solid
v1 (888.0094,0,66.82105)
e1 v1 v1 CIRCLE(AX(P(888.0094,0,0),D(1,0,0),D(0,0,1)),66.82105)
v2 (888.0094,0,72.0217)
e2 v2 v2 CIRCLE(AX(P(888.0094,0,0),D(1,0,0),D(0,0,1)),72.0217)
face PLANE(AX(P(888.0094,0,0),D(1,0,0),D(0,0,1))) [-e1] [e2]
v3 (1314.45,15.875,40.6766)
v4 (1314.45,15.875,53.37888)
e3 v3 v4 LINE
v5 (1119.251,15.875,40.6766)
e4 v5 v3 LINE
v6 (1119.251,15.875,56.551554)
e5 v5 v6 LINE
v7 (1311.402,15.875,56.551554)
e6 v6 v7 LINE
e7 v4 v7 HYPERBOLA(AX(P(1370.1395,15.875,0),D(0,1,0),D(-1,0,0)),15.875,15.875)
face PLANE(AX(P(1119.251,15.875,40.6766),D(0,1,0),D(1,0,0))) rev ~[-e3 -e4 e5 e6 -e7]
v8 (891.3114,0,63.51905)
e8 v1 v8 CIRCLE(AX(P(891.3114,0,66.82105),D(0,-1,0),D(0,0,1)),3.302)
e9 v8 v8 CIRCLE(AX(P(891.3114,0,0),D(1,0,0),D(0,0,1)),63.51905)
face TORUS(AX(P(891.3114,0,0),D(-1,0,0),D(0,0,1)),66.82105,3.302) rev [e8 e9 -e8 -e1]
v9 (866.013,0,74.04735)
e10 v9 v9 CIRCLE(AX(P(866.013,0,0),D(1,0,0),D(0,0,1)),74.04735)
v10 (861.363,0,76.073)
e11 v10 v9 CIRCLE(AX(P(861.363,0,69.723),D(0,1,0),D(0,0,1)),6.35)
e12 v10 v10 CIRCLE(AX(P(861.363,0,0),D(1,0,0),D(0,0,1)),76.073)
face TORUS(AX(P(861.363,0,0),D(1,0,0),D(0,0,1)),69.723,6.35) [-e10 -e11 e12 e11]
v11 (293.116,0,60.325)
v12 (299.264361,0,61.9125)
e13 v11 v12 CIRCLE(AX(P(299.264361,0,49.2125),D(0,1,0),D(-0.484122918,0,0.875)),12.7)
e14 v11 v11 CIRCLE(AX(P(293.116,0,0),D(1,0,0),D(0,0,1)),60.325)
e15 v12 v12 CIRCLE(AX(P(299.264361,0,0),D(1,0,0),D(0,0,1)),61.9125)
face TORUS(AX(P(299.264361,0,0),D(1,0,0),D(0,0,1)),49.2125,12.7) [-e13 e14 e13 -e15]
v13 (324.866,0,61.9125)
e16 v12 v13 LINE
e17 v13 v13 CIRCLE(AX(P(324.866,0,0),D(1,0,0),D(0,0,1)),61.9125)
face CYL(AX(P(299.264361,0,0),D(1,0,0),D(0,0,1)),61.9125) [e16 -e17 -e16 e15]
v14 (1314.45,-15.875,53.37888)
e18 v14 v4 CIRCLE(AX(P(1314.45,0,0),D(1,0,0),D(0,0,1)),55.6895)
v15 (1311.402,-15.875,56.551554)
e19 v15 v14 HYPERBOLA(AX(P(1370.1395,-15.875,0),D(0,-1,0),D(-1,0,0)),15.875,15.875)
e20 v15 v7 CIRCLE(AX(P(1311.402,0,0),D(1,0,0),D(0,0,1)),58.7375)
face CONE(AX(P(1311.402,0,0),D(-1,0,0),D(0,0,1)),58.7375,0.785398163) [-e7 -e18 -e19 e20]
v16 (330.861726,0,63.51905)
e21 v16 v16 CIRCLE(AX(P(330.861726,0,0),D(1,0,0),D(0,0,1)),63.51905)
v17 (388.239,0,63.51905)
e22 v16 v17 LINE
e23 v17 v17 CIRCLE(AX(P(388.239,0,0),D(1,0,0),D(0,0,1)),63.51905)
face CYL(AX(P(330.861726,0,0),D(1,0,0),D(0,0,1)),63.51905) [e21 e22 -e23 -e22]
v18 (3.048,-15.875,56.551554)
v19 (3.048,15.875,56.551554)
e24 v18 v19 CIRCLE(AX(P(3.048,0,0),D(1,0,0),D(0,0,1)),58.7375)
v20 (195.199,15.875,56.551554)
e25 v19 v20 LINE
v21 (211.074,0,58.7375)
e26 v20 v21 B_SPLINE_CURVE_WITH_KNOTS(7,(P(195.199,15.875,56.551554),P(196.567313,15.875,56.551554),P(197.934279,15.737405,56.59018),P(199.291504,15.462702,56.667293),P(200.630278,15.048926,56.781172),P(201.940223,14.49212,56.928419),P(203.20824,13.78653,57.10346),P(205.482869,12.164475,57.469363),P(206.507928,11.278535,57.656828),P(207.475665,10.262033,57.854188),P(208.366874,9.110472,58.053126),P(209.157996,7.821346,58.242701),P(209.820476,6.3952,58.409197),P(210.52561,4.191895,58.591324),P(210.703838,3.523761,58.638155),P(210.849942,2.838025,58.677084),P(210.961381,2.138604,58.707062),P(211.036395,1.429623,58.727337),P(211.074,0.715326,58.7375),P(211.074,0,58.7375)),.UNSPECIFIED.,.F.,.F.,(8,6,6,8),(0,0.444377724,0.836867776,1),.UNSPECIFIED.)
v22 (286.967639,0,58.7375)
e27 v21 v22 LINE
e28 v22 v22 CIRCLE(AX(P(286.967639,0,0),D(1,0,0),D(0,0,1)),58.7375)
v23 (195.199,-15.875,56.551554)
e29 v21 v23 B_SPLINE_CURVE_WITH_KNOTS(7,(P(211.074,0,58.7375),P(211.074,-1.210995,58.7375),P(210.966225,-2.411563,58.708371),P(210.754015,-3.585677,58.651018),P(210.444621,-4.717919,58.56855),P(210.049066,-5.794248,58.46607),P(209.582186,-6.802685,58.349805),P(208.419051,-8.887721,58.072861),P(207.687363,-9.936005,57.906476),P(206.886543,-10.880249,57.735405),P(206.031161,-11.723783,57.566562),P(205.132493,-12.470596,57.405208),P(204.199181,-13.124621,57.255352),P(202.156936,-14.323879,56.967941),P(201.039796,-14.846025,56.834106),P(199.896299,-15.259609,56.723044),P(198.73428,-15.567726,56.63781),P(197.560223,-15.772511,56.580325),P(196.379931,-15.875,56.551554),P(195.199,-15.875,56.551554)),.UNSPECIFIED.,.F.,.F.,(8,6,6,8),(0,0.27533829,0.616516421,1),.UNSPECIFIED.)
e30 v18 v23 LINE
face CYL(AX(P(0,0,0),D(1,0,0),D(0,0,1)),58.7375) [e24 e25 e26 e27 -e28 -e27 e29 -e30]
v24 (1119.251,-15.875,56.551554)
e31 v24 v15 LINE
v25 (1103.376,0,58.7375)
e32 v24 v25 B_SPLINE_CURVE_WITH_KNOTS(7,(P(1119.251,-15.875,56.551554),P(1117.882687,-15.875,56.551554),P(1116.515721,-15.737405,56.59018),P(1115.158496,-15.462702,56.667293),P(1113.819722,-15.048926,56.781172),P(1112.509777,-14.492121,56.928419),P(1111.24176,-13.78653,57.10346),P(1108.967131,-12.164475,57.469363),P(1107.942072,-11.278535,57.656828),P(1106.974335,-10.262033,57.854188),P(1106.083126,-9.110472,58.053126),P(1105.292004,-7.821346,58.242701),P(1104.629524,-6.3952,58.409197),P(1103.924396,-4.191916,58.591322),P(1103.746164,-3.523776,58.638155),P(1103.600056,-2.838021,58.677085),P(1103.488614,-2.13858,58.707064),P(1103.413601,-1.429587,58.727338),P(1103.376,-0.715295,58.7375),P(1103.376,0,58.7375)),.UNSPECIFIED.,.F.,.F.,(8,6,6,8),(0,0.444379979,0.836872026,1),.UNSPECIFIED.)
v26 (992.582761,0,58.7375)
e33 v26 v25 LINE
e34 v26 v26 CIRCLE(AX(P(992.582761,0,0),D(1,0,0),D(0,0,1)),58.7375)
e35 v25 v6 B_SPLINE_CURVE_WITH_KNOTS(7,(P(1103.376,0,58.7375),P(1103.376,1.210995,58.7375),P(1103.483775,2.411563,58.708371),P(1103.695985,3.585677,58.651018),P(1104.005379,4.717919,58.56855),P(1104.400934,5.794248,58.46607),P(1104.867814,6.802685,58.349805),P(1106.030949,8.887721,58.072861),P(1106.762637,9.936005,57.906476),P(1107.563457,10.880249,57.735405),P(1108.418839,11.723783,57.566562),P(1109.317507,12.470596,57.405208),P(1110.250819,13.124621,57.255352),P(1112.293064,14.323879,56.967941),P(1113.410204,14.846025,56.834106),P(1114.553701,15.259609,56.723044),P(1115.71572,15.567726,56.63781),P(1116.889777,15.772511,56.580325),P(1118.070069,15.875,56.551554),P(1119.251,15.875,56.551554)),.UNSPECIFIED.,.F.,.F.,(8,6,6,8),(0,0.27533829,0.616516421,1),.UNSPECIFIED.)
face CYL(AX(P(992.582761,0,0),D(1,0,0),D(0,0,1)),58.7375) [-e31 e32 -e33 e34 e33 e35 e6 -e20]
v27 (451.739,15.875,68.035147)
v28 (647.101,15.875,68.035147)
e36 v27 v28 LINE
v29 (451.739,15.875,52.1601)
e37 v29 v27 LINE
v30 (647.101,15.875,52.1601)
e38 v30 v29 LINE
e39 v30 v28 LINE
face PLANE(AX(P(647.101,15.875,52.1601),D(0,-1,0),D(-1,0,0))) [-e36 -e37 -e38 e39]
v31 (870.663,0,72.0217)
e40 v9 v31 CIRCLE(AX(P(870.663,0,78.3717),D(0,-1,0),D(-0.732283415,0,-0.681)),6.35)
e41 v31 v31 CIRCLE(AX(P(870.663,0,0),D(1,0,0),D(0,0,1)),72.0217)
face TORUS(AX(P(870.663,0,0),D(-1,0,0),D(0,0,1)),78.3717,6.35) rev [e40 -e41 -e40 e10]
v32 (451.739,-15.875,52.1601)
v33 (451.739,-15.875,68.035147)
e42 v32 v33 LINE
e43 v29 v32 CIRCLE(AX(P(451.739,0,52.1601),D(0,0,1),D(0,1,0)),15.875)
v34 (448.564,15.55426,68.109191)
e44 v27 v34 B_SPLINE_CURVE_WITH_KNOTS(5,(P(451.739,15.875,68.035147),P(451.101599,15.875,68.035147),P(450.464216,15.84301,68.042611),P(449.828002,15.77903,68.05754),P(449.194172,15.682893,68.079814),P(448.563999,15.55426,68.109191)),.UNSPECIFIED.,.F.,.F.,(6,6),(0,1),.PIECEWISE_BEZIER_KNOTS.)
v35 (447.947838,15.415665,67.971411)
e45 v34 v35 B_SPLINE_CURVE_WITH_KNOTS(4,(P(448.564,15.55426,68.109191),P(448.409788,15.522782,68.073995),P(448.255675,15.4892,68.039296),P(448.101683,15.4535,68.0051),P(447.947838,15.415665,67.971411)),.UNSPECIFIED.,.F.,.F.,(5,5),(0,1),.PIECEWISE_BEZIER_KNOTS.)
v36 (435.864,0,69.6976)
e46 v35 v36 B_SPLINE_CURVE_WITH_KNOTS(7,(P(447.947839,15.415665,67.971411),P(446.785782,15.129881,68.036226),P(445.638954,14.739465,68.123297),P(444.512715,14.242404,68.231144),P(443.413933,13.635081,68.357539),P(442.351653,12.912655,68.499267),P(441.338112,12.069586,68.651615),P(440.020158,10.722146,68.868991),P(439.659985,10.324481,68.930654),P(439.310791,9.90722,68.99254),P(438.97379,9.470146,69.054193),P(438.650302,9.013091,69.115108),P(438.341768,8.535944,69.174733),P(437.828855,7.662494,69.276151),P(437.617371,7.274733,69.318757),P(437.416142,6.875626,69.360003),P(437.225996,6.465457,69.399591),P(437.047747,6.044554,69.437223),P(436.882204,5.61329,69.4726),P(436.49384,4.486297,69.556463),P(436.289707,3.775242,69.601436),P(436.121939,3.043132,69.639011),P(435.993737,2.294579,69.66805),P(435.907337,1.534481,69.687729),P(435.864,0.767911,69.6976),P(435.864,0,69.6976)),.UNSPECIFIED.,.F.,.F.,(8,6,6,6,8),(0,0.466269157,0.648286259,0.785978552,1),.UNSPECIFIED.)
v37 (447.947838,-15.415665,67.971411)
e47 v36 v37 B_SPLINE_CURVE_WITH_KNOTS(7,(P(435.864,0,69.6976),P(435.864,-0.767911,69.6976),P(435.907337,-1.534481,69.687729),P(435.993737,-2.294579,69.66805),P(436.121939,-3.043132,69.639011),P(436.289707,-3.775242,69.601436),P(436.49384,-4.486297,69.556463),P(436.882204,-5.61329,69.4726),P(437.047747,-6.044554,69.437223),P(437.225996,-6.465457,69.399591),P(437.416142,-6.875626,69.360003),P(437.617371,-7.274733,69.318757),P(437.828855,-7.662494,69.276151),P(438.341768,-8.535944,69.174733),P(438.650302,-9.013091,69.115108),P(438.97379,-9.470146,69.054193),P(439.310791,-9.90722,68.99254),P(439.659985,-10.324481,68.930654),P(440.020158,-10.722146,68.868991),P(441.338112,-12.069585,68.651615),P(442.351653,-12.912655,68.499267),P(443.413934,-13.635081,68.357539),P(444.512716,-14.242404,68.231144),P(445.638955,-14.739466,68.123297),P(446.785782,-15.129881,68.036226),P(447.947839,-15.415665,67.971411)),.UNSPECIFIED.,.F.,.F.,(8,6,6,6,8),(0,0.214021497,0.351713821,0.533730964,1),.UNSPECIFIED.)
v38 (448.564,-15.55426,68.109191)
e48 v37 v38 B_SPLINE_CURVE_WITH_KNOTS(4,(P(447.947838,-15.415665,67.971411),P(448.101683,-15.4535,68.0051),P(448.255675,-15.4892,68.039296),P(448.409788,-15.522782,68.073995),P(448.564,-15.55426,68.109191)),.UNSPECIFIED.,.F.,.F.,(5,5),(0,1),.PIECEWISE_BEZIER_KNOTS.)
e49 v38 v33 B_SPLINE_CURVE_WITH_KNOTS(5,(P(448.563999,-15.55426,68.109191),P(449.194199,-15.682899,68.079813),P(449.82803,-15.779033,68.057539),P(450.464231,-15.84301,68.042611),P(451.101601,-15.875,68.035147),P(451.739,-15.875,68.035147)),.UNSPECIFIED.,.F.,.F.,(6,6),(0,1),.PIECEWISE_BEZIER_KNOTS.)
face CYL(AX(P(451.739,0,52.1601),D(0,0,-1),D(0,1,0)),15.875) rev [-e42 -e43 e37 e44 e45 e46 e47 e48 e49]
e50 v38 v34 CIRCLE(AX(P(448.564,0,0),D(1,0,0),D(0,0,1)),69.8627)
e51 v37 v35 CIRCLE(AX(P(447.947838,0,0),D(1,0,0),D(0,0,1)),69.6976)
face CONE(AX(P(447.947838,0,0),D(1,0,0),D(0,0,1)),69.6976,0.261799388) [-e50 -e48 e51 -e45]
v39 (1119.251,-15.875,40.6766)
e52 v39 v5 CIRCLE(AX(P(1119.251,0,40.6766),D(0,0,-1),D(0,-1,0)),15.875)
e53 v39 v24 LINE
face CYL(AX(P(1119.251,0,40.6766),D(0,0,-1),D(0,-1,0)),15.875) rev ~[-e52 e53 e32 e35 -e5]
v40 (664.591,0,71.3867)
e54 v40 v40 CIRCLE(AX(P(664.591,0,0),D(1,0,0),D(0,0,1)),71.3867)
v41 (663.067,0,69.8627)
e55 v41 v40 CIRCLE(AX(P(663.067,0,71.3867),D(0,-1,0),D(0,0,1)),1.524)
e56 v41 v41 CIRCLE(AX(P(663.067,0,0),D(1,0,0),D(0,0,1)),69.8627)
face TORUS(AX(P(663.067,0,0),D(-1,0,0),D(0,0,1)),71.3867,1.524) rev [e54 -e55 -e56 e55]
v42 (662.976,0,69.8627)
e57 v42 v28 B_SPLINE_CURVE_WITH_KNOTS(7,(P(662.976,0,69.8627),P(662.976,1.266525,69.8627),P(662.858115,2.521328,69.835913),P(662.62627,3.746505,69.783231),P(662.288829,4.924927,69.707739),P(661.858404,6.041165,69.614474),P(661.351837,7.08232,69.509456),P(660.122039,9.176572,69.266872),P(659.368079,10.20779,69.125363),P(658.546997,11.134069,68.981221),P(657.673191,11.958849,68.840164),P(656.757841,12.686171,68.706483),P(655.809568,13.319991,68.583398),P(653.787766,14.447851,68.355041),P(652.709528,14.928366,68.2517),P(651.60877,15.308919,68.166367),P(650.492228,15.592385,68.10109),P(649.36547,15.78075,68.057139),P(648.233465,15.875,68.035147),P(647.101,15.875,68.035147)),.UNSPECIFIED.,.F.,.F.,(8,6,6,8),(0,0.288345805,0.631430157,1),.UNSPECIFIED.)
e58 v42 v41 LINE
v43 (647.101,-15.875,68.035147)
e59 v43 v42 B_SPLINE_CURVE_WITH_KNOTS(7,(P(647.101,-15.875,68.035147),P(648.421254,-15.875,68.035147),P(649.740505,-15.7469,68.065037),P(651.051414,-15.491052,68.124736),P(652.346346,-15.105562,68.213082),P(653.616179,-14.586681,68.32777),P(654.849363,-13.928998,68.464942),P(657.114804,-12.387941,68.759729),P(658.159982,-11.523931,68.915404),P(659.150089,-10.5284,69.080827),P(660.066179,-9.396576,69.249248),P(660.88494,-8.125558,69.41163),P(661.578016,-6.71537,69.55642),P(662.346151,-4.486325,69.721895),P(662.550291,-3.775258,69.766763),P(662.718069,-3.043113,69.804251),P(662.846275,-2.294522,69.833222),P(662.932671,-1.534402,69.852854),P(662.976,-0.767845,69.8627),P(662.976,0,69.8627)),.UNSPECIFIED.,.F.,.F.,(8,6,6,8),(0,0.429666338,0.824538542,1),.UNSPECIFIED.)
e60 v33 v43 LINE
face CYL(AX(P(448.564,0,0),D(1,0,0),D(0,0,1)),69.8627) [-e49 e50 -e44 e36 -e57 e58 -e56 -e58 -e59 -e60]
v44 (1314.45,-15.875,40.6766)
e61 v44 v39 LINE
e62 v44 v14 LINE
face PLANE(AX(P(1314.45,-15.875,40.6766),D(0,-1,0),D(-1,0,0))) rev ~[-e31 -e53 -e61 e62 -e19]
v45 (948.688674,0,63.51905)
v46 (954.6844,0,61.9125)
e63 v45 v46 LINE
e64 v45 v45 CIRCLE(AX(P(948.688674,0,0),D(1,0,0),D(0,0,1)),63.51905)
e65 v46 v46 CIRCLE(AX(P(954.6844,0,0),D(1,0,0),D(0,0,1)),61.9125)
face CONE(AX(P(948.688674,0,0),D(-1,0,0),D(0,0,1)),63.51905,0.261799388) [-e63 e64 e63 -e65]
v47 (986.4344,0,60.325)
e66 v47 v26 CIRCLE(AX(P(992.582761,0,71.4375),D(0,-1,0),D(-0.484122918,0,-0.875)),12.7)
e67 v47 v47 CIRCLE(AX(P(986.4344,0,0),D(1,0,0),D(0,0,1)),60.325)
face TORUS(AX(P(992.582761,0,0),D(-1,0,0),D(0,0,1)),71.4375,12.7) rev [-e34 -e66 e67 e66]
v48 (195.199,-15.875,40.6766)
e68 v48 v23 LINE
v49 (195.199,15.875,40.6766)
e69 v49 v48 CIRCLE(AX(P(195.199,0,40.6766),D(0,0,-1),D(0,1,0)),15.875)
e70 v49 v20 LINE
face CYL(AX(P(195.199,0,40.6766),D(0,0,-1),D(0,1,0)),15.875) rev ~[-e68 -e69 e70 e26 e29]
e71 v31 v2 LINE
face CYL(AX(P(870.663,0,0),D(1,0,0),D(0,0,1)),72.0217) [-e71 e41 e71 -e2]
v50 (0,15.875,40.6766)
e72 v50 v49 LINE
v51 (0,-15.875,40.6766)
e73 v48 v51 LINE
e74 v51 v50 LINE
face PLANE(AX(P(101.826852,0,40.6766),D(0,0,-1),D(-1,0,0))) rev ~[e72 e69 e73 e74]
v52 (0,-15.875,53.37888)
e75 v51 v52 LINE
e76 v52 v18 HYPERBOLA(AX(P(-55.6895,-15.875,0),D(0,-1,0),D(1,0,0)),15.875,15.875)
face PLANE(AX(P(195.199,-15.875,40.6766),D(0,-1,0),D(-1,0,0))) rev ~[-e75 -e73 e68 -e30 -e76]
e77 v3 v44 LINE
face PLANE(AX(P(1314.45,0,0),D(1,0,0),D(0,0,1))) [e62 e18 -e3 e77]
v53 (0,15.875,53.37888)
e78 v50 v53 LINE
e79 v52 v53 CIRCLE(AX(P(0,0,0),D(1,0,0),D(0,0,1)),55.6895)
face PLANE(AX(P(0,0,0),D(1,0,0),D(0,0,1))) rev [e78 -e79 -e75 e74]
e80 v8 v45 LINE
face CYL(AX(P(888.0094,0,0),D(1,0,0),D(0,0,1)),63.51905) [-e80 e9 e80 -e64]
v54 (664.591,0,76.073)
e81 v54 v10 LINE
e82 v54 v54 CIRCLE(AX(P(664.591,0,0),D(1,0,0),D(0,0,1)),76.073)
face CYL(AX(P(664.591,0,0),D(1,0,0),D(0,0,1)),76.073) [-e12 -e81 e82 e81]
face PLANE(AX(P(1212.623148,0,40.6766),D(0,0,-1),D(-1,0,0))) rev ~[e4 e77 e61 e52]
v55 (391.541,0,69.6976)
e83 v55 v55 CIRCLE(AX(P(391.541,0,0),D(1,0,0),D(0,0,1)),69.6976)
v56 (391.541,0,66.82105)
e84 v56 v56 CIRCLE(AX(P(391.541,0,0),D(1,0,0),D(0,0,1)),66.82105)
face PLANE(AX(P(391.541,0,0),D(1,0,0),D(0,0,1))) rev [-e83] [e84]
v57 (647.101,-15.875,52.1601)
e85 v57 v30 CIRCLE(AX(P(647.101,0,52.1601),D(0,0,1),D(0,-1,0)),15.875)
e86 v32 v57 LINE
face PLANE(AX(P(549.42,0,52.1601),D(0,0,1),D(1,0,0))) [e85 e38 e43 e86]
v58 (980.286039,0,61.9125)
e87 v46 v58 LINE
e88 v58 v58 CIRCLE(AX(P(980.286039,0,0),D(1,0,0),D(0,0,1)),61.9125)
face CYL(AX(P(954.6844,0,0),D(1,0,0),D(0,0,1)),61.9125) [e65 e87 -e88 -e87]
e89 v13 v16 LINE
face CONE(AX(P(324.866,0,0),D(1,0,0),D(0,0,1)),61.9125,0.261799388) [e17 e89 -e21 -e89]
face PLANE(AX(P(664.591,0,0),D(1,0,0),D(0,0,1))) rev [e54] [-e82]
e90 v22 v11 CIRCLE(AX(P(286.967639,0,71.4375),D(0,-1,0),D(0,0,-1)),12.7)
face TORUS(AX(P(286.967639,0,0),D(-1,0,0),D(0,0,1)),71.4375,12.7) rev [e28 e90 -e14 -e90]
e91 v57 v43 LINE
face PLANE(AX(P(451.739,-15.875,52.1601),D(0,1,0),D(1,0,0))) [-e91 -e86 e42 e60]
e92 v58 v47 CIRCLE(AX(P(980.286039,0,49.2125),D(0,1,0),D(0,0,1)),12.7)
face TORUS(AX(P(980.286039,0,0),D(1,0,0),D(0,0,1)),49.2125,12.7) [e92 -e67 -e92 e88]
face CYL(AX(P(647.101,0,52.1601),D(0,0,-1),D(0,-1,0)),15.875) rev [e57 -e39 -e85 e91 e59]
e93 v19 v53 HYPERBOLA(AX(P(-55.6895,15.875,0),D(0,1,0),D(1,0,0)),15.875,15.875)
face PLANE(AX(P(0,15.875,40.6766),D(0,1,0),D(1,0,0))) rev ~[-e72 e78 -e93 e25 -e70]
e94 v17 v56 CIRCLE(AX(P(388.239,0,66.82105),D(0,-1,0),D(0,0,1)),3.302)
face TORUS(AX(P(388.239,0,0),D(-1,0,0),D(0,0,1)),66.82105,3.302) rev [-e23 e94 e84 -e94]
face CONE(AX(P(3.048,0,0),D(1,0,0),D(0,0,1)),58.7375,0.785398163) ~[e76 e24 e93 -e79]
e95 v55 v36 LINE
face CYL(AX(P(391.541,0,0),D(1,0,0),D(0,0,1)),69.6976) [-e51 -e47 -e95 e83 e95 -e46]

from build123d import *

# Parameters (mm, degrees)
FILLET3_R      = 3.302
FILLET4_R      = 1.524
CHAMFER1_SIZE  = 3.048
EXTRUDE1_START = 40.6766
EXTRUDE1_DEPTH = 1279.168730275
EXTRUDE2_START = 52.1601
EXTRUDE2_DEPTH = 1267.685230275


with BuildPart() as part:
    # Sketch1 → Revolve1 (revolve)
    with BuildSketch(Plane.XY, mode=Mode.PRIVATE) as revolve1_sk:
        with BuildLine():
            Line((0, 0), (0, 58.7375))
            Line((0, 58.7375), (286.967638938, 58.7375))
            ThreePointArc((286.967638938, 58.7375), (290.142638938, 59.140777876), (293.116, 60.325))
            ThreePointArc((293.116, 60.325), (296.089361062, 61.509222124), (299.264361062, 61.9125))
            Line((299.264361062, 61.9125), (324.866, 61.9125))
            Line((324.866, 61.9125), (330.861726225, 63.51905))
            Line((330.861726225, 63.51905), (391.541, 63.51905))
            Line((391.541, 63.51905), (391.541, 69.6976))
            Line((391.541, 69.6976), (447.947838412, 69.6976))
            Line((447.947838412, 69.6976), (448.564, 69.8627))
            Line((448.564, 69.8627), (664.591, 69.8627))
            Line((664.591, 69.8627), (664.591, 76.073))
            Line((664.591, 76.073), (861.363000314, 76.073))
            ThreePointArc((861.363000314, 76.073), (863.899028459, 75.544602979), (866.013, 74.04735))
            ThreePointArc((866.013, 74.04735), (868.126971541, 72.550097021), (870.662999686, 72.0217))
            Line((870.662999686, 72.0217), (888.0094, 72.0217))
            Line((888.0094, 72.0217), (888.0094, 63.51905))
            Line((888.0094, 63.51905), (948.688673775, 63.51905))
            Line((948.688673775, 63.51905), (954.6844, 61.9125))
            Line((954.6844, 61.9125), (980.286038938, 61.9125))
            ThreePointArc((980.286038938, 61.9125), (983.461038938, 61.509222124), (986.4344, 60.325))
            ThreePointArc((986.4344, 60.325), (989.407761062, 59.140777876), (992.582761062, 58.7375))
            Line((992.582761062, 58.7375), (1314.45, 58.7375))
            Line((1314.45, 58.7375), (1314.45, 0))
            Line((1314.45, 0), (0, 0))
        make_face()
    revolve(revolve1_sk.sketch.rotate(Axis((0, 0, 0), (1, 0, 0)), 90), axis=Axis((0, 0, 0), (1, 0, 0)))

    # Fillet3
    fillet3_edges = [part.edges().sort_by_distance(p)[0] for p in [
        (391.541, 0, -63.51905),
        (888.0094, 0, -63.51905),
    ]]
    fillet(fillet3_edges, radius=FILLET3_R)

    # Fillet4
    fillet4_edges = [part.edges().sort_by_distance(p)[0] for p in [
        (664.591, 0, -69.8627),
    ]]
    fillet(fillet4_edges, radius=FILLET4_R)

    # Chamfer1
    chamfer1_edges = [part.edges().sort_by_distance(p)[0] for p in [
        (0, 0, -58.7375),
        (1314.45, 0, -58.7375),
    ]]
    chamfer(chamfer1_edges, length=CHAMFER1_SIZE)

    # Sketch2 → Extrude1 (cut, through all)
    with BuildSketch(Plane.XY.offset(EXTRUDE1_START)):
        with BuildLine():
            Line((0, 15.875), (195.199, 15.875))
            ThreePointArc((195.199, 15.875), (211.074, 0), (195.199, -15.875))
            Line((195.199, -15.875), (0, -15.875))
            Line((0, -15.875), (0, 15.875))
        make_face()
        with BuildLine():
            Line((1314.45, 15.875), (1314.45, -15.875))
            Line((1314.45, -15.875), (1119.251, -15.875))
            ThreePointArc((1119.251, -15.875), (1103.376, 0), (1119.251, 15.875))
            Line((1119.251, 15.875), (1314.45, 15.875))
        make_face()
    extrude(amount=EXTRUDE1_DEPTH, mode=Mode.SUBTRACT)

    # Sketch3 → Extrude2 (cut, through all)
    with BuildSketch(Plane.XY.offset(EXTRUDE2_START)):
        with BuildLine():
            Line((451.739, -15.875), (647.101, -15.875))
            ThreePointArc((647.101, -15.875), (662.976, 0), (647.101, 15.875))
            Line((647.101, 15.875), (451.739, 15.875))
            ThreePointArc((451.739, 15.875), (435.864, 0), (451.739, -15.875))
        make_face()
    extrude(amount=EXTRUDE2_DEPTH, mode=Mode.SUBTRACT)


solid = part.part
